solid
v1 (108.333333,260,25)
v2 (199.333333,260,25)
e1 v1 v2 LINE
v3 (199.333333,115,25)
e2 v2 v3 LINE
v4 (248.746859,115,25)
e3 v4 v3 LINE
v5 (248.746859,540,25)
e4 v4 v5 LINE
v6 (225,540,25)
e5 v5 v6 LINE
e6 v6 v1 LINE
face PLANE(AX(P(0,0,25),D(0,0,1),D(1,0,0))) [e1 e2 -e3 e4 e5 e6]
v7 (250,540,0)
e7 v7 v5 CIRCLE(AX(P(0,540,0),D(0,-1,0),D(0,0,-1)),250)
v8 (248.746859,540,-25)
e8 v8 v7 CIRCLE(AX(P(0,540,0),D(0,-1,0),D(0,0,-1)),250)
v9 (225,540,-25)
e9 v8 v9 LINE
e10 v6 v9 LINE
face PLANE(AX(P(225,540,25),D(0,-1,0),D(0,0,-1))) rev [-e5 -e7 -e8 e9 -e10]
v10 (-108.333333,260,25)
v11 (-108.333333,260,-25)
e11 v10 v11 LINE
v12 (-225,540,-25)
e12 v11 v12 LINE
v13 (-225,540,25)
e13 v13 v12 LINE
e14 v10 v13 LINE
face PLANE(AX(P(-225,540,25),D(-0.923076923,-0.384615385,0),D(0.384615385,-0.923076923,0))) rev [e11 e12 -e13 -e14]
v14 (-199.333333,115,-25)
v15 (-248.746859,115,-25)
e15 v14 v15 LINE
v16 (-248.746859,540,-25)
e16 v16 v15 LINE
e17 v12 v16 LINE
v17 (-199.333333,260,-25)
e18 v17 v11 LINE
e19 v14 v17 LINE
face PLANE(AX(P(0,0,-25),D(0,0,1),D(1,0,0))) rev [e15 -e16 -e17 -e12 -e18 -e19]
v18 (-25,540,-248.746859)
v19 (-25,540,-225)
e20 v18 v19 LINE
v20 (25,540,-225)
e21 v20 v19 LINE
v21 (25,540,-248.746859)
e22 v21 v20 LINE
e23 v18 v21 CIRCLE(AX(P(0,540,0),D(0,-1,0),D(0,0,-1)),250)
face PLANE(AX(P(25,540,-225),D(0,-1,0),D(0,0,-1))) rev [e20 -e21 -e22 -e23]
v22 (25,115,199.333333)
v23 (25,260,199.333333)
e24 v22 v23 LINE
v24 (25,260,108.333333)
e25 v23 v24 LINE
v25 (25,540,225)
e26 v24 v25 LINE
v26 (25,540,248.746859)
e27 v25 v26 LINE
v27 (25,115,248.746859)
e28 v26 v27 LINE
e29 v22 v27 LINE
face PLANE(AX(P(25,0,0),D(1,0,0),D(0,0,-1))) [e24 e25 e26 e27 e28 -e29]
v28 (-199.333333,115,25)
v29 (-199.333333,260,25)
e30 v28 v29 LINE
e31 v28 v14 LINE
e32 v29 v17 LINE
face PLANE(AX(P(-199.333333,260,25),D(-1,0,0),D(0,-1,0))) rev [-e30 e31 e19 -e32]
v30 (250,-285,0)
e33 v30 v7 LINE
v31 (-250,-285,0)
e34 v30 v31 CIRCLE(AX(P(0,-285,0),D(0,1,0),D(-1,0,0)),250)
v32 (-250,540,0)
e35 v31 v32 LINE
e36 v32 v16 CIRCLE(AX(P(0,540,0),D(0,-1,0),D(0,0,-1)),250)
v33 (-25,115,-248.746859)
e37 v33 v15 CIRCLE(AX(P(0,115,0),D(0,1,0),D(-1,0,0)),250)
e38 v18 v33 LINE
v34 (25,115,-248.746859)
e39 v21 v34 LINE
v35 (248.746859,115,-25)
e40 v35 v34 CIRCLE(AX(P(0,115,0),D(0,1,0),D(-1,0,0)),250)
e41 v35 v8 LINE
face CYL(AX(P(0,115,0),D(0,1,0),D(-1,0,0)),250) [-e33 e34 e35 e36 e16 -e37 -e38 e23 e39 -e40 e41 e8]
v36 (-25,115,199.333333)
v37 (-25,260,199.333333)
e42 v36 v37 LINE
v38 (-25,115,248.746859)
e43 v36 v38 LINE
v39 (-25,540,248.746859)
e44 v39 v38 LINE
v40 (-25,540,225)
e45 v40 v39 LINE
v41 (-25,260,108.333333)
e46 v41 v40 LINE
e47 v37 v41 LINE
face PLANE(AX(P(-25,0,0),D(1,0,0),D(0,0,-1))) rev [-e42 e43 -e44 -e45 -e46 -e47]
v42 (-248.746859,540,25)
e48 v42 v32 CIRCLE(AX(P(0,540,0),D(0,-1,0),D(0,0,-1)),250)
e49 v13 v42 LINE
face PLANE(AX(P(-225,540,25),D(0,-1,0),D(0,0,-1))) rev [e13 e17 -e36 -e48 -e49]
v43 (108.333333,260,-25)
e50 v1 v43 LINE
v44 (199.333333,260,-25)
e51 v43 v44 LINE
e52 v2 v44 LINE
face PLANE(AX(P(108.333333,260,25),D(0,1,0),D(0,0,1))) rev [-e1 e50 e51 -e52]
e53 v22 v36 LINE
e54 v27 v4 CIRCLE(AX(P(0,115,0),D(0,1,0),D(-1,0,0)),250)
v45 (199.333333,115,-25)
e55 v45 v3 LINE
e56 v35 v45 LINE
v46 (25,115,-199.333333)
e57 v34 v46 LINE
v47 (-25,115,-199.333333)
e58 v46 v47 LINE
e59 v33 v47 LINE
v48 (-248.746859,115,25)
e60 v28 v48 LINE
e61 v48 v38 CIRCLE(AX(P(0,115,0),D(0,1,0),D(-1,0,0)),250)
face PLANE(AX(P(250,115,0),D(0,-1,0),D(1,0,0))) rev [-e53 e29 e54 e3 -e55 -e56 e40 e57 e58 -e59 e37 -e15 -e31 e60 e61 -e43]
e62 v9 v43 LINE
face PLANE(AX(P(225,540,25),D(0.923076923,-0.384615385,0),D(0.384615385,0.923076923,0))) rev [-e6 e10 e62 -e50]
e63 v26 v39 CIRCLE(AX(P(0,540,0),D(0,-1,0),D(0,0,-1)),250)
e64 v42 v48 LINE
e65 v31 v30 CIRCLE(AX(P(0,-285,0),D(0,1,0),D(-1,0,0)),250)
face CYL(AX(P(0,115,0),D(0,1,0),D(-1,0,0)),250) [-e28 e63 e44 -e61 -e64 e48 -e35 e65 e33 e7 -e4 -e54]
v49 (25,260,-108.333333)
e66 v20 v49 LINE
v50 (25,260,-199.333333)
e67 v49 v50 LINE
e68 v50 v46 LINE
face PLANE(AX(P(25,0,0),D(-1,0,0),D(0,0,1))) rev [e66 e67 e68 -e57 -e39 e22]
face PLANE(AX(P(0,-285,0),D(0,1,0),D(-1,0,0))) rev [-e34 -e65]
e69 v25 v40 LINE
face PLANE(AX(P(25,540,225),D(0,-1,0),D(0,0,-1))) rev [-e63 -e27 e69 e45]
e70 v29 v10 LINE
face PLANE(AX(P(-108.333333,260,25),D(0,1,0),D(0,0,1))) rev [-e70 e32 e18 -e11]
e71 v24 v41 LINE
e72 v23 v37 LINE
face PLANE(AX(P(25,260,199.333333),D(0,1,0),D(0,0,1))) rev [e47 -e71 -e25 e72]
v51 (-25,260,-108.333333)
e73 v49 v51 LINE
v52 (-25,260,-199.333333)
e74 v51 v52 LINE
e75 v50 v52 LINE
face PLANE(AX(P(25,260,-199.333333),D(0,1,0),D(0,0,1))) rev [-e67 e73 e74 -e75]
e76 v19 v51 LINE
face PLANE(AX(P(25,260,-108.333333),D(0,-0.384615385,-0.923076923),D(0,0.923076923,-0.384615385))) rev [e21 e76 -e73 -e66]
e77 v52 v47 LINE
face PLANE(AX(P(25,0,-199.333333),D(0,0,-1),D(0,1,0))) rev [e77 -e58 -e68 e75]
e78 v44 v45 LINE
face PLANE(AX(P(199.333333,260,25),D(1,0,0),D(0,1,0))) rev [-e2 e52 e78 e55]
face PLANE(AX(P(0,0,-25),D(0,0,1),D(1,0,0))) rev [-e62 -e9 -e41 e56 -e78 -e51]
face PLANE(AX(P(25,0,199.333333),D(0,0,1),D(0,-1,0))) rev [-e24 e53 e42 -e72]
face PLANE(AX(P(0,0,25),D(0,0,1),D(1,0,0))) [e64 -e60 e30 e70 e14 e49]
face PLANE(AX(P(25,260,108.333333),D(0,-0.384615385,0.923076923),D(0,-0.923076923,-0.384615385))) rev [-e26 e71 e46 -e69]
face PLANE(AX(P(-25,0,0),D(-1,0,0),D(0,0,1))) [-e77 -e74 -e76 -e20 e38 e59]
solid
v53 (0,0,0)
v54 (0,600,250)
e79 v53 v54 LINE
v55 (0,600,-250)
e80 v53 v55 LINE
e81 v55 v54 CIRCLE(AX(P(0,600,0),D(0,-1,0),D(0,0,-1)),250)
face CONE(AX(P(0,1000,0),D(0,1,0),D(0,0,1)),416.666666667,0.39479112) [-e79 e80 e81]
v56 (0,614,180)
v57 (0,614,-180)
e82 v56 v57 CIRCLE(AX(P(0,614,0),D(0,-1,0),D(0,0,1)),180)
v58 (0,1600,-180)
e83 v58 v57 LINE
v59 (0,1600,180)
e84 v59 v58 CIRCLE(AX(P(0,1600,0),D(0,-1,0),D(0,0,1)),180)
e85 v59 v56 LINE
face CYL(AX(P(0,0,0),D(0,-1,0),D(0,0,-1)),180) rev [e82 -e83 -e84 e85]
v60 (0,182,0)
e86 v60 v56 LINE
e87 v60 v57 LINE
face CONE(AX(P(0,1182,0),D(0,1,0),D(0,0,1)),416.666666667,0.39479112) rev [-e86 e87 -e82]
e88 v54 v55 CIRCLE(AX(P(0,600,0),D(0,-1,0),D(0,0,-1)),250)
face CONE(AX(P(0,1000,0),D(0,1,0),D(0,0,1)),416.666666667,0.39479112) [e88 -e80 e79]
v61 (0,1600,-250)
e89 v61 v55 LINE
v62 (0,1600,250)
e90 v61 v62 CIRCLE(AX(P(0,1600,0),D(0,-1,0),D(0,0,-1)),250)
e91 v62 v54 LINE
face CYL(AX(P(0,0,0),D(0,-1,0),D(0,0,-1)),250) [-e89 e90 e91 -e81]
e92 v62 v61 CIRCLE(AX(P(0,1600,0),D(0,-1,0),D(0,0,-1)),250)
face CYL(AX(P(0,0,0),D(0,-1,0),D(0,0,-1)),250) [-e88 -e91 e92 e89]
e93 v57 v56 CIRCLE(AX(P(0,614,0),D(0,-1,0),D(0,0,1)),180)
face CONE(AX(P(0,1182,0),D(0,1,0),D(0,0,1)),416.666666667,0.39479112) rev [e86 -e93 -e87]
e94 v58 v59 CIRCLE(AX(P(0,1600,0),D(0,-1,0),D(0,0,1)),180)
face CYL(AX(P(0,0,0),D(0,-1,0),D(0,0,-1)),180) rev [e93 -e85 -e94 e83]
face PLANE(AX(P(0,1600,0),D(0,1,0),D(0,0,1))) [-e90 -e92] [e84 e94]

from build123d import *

# Parameters (mm, degrees)
SHELL1_T              = -70
BOSS_EXTRUDE1_DEPTH   = 25
BOSS_EXTRUDE1_2_DEPTH = 25
BOSS_EXTRUDE2_DEPTH   = 25
BOSS_EXTRUDE2_2_DEPTH = 25
SKETCH4_W             = 250
SKETCH4_H             = 400
SKETCH5_OUTSIDE_W     = 904.652
SKETCH5_OUTSIDE_H     = 904.652
SKETCH5_OUTSIDE_R     = 250
CUT_EXTRUDE1_DEPTH    = 1918.869912168


with BuildPart() as part:
    # Sketch1 → Revolve1 (revolve)
    with BuildSketch(Plane.XY, mode=Mode.PRIVATE) as revolve1_sk:
        Polygon((0, 0), (0, 1600), (250, 1600), (250, 600), align=None)
    revolve(revolve1_sk.sketch.rotate(Axis((0, 0, 0), (0, 1, 0)), 270), axis=Axis((0, 0, 0), (0, 1, 0)))

    # Shell1
    shell1_openings = [part.faces().sort_by_distance(p)[0] for p in [
        (0, 1600, 0),
    ]]
    offset(amount=SHELL1_T, openings=shell1_openings, kind=Kind.INTERSECTION)


with BuildPart() as body_2:
    # Sketch2 → Boss-Extrude1 (new, symmetric)
    with BuildSketch(Plane.XY):
        Polygon((-108.333333333, 260), (-199.333333333, 260), (-199.333333333, 0), (-250, 0), (-250, 540), (-225, 540), align=None)
    extrude(amount=BOSS_EXTRUDE1_DEPTH, both=True)


with BuildPart() as body_3:
    # Sketch2 → Boss-Extrude1 2 (new, symmetric)
    with BuildSketch(Plane.XY):
        Polygon((225, 540), (108.333333333, 260), (199.333333333, 260), (199.333333333, 0), (250, 0), (250, 540), align=None)
    extrude(amount=BOSS_EXTRUDE1_2_DEPTH, both=True)


with BuildPart() as body_4:
    # Sketch3 → Boss-Extrude2 (new, symmetric)
    with BuildSketch(Plane(origin=(0, 0, 0), x_dir=(0, 0, -1), z_dir=(1, 0, 0))):
        Polygon((-250, 0), (-199.333333333, 0), (-199.333333333, 260), (-108.333333333, 260), (-225, 540), (-250, 540), align=None)
    extrude(amount=BOSS_EXTRUDE2_DEPTH, both=True)


with BuildPart() as body_5:
    # Sketch3 → Boss-Extrude2 2 (new, symmetric)
    with BuildSketch(Plane(origin=(0, 0, 0), x_dir=(0, 0, -1), z_dir=(1, 0, 0))):
        Polygon((108.333333333, 260), (225, 540), (250, 540), (250, 0), (199.333333333, 0), (199.333333333, 260), align=None)
    extrude(amount=BOSS_EXTRUDE2_2_DEPTH, both=True)


    add(body_4.part)  # Revolve2 merges body 4

    add(body_3.part)  # Revolve2 merges body 3

    add(body_2.part)  # Revolve2 merges body 2
    # Sketch4 → Revolve2 (revolve)
    with BuildSketch(Plane.XY, mode=Mode.PRIVATE) as revolve2_sk:
        with Locations((125, -85)):
            Rectangle(SKETCH4_W, SKETCH4_H)
    revolve(revolve2_sk.sketch.rotate(Axis((0, 115, 0), (0, -1, 0)), 180), axis=Axis((0, 115, 0), (0, -1, 0)))

    # Sketch5 outside → Cut-Extrude1 (cut, through all)
    with BuildSketch(Plane.XZ.offset(285)):
        Rectangle(SKETCH5_OUTSIDE_W, SKETCH5_OUTSIDE_H)
        with Locations(Location((0, 0, 0), (0, 0, 180))):
            Circle(SKETCH5_OUTSIDE_R, mode=Mode.SUBTRACT)
    extrude(amount=-CUT_EXTRUDE1_DEPTH, mode=Mode.SUBTRACT)


solid = Compound([part.part, body_5.part])
